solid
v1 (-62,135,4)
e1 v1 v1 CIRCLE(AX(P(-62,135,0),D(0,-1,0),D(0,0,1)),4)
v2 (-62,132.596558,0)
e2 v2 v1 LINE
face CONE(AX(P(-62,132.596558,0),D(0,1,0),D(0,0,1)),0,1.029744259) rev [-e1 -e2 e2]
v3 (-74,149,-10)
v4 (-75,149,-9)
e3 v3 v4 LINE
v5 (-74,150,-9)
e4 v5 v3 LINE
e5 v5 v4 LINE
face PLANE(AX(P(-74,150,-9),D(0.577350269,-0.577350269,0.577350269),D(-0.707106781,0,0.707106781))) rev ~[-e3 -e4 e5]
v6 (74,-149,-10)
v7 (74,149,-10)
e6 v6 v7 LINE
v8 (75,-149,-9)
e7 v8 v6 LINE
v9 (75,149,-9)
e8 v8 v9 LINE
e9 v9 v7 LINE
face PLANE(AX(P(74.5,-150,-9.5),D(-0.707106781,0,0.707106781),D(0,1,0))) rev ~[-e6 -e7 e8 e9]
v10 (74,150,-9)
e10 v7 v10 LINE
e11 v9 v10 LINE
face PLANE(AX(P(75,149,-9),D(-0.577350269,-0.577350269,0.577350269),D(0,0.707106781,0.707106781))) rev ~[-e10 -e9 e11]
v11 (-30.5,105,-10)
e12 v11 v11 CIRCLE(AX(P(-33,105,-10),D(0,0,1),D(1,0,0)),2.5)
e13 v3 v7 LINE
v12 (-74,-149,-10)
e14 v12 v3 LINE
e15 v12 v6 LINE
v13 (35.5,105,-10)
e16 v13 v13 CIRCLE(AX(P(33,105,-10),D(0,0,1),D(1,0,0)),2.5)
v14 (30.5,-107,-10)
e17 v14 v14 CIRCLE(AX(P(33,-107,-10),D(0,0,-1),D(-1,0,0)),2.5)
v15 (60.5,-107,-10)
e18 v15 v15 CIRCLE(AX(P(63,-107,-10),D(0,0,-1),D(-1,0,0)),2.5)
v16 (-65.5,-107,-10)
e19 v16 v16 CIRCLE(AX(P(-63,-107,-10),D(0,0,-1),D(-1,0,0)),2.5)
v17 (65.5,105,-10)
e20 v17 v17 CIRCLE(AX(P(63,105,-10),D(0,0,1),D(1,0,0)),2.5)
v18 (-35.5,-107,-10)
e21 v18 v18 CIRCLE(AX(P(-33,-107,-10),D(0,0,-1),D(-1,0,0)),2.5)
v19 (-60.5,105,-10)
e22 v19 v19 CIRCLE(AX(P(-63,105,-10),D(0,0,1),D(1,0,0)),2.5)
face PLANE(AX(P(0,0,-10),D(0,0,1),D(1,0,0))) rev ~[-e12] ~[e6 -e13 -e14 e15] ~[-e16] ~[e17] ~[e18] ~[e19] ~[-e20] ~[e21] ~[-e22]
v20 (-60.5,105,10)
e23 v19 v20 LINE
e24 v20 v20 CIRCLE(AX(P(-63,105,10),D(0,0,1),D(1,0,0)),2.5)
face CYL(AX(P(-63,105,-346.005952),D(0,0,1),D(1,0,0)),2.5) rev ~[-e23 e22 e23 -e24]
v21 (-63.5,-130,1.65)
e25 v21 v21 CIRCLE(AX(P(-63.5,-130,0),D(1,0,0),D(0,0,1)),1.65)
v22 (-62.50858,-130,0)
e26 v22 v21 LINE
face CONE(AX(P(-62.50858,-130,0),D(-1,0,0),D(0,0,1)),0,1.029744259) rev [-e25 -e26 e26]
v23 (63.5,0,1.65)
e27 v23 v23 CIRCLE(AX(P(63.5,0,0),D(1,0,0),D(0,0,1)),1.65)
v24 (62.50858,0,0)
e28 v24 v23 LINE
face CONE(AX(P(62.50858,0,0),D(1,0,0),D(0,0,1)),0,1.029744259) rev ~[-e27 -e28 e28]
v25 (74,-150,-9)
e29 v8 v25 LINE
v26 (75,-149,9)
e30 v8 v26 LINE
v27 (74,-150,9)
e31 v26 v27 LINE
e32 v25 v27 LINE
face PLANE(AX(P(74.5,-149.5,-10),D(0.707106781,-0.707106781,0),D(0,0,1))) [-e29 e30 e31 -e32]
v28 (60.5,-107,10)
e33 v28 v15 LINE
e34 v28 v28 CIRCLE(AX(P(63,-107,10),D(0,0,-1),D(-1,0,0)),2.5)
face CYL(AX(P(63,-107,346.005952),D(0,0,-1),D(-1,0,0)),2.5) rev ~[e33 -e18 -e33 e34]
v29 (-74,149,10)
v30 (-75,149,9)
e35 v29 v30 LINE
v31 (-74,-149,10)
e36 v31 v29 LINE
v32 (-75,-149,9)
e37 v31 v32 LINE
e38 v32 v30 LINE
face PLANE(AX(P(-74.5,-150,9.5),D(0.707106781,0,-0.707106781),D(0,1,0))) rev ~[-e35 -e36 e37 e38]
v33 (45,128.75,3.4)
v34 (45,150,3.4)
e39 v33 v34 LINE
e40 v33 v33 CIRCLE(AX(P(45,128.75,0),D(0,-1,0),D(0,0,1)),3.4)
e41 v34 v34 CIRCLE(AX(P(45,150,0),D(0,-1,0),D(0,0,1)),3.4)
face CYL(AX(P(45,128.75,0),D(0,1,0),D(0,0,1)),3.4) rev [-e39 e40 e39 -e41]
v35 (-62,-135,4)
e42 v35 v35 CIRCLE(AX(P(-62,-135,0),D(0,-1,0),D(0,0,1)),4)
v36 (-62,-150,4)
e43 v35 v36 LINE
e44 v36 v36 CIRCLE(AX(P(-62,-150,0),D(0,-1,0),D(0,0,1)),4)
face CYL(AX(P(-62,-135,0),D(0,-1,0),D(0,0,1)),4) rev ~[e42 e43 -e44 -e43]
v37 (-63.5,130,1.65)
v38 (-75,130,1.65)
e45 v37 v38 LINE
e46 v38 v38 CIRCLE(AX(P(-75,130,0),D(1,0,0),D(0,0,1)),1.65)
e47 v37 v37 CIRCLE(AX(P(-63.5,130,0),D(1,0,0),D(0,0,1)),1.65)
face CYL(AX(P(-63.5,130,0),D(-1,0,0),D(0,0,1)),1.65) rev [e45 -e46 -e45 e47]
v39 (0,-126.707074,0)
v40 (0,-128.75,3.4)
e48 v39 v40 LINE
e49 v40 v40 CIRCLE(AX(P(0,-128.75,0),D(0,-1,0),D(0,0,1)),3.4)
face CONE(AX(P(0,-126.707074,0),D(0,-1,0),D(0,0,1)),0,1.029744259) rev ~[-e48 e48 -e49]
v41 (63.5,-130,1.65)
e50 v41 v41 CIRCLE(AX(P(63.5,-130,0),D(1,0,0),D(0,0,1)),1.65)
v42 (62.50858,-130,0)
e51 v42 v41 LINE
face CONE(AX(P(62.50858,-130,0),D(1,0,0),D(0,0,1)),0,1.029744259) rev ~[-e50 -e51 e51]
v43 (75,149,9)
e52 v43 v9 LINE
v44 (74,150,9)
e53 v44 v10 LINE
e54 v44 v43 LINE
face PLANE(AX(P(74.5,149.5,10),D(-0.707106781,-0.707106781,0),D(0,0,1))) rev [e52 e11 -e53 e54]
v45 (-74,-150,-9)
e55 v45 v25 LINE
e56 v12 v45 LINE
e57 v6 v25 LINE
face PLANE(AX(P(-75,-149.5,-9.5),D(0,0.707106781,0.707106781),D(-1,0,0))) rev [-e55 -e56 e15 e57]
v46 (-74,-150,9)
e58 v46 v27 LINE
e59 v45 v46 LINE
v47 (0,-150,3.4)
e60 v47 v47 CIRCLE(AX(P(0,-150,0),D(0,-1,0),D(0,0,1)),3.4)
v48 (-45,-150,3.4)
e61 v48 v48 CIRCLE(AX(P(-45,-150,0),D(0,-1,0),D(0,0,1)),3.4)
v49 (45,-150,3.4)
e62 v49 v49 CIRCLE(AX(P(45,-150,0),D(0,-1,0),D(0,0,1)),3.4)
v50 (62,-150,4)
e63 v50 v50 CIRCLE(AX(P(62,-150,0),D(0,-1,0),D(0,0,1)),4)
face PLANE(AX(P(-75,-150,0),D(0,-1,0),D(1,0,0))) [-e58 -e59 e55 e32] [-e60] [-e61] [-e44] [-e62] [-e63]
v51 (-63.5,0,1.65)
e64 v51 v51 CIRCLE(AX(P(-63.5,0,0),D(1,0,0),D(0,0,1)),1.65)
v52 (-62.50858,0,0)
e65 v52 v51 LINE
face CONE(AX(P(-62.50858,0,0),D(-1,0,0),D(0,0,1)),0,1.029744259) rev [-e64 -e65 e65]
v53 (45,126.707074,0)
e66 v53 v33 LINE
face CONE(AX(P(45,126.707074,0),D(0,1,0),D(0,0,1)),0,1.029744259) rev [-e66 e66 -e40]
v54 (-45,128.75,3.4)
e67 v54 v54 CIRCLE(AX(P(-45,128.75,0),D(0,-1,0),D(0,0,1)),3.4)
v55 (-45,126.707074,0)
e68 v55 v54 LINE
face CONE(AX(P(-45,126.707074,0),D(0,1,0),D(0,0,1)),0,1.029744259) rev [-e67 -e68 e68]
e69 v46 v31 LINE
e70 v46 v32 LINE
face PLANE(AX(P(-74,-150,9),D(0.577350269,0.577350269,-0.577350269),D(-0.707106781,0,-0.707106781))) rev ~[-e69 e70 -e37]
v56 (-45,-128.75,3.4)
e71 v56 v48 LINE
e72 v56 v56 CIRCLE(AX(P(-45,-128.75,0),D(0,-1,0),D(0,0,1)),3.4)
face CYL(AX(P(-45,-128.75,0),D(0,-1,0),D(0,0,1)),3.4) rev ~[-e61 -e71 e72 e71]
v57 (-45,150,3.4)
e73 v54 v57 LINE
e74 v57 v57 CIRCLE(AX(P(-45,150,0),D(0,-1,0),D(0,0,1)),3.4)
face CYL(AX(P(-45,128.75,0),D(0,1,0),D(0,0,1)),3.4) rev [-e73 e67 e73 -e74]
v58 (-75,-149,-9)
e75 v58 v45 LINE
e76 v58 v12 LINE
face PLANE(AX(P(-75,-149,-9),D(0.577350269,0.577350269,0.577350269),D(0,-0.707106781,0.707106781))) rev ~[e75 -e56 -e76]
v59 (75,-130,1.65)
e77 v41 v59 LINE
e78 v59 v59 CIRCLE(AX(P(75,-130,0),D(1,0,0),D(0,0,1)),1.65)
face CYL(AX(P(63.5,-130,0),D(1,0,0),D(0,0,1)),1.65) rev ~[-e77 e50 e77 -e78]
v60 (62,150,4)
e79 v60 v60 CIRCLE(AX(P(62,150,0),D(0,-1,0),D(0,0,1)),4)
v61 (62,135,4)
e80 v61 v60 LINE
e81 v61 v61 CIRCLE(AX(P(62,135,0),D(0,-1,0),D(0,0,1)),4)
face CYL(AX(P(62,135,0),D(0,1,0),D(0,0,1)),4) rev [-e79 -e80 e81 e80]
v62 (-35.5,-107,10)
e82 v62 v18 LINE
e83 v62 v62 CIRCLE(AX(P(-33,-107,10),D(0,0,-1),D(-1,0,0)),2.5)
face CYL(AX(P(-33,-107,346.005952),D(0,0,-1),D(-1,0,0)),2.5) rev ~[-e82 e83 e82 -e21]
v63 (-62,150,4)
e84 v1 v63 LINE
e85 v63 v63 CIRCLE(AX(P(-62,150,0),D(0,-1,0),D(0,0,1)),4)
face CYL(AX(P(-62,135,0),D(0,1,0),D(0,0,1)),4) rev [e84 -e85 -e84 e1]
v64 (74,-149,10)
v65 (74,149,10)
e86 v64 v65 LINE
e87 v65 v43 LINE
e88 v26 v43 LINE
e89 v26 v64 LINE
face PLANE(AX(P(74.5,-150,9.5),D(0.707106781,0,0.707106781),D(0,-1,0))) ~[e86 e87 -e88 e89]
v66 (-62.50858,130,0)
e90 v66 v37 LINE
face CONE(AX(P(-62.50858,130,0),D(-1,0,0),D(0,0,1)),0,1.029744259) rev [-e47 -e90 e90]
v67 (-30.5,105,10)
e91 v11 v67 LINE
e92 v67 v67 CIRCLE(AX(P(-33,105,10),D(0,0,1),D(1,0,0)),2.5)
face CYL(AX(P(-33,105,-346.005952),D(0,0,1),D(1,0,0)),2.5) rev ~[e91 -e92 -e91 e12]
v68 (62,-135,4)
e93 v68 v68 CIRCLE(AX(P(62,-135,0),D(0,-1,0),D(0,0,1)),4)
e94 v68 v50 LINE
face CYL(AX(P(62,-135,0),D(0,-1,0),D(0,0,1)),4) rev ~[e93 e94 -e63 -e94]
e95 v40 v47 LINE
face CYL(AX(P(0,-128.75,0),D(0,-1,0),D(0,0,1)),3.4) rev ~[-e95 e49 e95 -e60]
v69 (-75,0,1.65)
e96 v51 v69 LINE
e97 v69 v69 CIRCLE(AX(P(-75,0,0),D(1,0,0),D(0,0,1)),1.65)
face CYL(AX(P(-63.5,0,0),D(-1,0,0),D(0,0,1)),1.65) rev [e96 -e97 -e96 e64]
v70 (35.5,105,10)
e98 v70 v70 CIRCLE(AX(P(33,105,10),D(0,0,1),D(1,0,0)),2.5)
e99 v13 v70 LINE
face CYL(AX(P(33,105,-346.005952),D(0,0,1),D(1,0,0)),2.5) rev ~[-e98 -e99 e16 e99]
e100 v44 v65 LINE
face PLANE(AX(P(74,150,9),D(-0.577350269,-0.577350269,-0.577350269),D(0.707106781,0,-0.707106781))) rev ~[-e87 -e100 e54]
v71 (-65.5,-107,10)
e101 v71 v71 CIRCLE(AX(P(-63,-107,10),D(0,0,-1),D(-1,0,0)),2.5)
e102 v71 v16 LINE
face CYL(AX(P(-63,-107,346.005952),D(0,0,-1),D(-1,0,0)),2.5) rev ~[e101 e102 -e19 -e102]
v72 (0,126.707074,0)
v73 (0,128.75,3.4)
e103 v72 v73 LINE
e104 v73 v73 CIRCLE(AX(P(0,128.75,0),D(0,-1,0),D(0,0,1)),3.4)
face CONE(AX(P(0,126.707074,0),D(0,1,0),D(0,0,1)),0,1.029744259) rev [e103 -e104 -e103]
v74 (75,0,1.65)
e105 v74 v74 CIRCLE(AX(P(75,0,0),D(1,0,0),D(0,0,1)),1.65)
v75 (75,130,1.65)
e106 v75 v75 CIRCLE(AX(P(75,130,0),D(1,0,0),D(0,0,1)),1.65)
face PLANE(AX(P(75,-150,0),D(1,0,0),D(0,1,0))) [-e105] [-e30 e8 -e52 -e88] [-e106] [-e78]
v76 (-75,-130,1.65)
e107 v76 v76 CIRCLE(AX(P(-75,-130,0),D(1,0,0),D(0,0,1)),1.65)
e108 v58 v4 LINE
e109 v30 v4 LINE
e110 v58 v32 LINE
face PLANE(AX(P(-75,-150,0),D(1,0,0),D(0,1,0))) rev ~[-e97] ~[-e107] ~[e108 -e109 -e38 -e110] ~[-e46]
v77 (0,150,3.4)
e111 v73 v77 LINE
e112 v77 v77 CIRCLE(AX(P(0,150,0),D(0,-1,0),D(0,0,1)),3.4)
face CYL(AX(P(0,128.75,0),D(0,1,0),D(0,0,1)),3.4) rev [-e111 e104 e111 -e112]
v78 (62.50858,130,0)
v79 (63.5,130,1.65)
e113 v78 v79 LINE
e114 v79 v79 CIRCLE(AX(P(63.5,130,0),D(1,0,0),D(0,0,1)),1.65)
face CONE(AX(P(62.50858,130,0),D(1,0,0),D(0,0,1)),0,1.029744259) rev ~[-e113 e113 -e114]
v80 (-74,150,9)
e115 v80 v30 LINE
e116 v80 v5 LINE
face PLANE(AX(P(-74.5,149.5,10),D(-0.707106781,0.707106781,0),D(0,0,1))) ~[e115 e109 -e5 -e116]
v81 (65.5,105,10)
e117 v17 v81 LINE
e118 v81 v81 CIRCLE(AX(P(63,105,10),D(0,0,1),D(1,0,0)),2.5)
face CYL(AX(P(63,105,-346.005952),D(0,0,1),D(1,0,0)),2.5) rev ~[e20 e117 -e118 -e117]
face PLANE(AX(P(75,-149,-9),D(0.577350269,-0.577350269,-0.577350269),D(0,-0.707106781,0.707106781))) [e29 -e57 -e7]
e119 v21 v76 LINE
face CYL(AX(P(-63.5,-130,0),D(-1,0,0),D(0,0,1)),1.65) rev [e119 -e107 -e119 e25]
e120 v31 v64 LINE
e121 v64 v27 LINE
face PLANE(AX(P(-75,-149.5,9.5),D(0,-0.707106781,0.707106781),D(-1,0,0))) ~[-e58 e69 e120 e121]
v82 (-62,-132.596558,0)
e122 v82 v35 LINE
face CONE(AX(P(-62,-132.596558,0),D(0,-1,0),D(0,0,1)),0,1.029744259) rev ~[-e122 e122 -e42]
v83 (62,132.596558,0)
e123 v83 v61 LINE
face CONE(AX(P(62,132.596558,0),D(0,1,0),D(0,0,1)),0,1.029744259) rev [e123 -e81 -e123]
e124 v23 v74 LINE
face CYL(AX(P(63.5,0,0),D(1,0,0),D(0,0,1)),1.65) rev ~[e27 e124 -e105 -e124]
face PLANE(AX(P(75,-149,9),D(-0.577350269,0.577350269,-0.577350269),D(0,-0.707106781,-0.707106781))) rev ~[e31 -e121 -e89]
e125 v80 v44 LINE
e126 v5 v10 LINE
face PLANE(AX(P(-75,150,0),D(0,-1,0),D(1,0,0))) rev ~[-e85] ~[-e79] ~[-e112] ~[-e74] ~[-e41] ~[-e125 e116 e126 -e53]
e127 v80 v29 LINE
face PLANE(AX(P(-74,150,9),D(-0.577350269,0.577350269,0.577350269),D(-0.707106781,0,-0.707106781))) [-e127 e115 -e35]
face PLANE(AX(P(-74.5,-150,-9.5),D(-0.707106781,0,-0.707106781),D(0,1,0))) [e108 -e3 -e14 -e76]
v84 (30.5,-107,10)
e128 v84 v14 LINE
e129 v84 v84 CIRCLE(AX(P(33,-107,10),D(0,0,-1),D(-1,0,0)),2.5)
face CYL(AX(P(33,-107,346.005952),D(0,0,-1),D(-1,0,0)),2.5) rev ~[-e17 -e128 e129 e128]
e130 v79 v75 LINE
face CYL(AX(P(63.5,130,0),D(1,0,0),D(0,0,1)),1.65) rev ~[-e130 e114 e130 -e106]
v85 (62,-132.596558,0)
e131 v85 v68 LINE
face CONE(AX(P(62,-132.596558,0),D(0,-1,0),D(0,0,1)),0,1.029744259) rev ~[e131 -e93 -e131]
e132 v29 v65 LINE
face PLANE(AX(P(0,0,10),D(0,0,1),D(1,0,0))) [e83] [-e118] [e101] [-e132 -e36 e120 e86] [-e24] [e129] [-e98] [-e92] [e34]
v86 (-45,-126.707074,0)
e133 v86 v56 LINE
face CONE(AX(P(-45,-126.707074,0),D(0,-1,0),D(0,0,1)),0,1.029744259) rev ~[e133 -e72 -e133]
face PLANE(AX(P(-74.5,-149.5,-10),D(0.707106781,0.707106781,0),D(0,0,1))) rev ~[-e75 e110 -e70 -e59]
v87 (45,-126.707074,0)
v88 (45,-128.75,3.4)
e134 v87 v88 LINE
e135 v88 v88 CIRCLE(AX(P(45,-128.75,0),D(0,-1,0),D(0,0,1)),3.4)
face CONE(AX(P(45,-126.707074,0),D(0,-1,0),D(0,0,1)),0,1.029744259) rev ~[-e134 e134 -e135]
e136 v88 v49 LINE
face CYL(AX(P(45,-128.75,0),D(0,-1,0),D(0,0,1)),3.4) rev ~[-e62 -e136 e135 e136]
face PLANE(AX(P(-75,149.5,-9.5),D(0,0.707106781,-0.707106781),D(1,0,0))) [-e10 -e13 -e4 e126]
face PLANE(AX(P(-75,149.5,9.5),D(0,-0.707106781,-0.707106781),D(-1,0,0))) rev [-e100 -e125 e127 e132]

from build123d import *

# Parameters (mm, degrees)
SKETCH_1_W                  = 150
SKETCH_1_H                  = 300
EXTRUDE_1_DEPTH             = 10
CHAMFER_1_SIZE              = 1
HOLE_WIZARD_M8_1_AT_2_COUNT = 2
HOLE_WIZARD_M8_1_AT_2_PITCH = 90
HOLE_WIZARD_M8_1_AT_3_COUNT = 2
HOLE_WIZARD_M8_1_AT_3_PITCH = 45
HOLE_WIZARD_M4_1_AT_2_COUNT = 2
HOLE_WIZARD_M4_1_AT_2_PITCH = 130
HOLE_WIZARD_M4_1_AT_3_COUNT = 2
HOLE_WIZARD_M4_1_AT_3_PITCH = 260
MM_1_AT_2_COUNT             = 2
MM_1_AT_2_PITCH             = 124
HOLE_WIZARD_M6_3_D          = 5
HOLE_WIZARD_M6_4_D          = 5


with BuildPart() as part:
    # 草图1 → 凸台-拉伸1 (new, symmetric)
    with BuildSketch(Plane.XY):
        Rectangle(SKETCH_1_W, SKETCH_1_H)
    extrude(amount=EXTRUDE_1_DEPTH, both=True)

    # 倒角1
    chamfer_1_edges = [part.edges().sort_by_distance(p)[0] for p in [
        (-75, 0, 10),
        (0, -150, 10),
        (75, 0, 10),
        (0, -150, -10),
        (-75, 0, -10),
        (0, 150, -10),
        (75, 0, -10),
        (0, 150, 10),
        (75, -150, 0),
        (-75, -150, 0),
        (-75, 150, 0),
        (75, 150, 0),
    ]]
    chamfer(chamfer_1_edges, length=CHAMFER_1_SIZE)

    # 草图2 → M8 螺纹孔1 (revolve, cut)
    with BuildSketch(Plane(origin=(-45, 150, 0), x_dir=(0, 0, 1), z_dir=(1, 0, 0))):
        Polygon((0, 0), (0, 23.292926105), (3.4, 21.25), (3.4, 0), align=None)
    hole_wizard_m8_1 = revolve(axis=Axis((-45, 156.35, 0), (0, -1, 0)), mode=Mode.SUBTRACT)

    # M8 螺纹孔1 at 2: M8 螺纹孔1 ×2
    with Locations(*[(i * HOLE_WIZARD_M8_1_AT_2_PITCH, 0, 0) for i in range(1, HOLE_WIZARD_M8_1_AT_2_COUNT)]):
        add(hole_wizard_m8_1, mode=Mode.SUBTRACT)

    # M8 螺纹孔1 at 3: M8 螺纹孔1 ×2
    with Locations(*[(i * HOLE_WIZARD_M8_1_AT_3_PITCH, 0, 0) for i in range(1, HOLE_WIZARD_M8_1_AT_3_COUNT)]):
        add(hole_wizard_m8_1, mode=Mode.SUBTRACT)

    # 草图10 → M4 螺纹孔1 (revolve, cut)
    with BuildSketch(Plane(origin=(-75, -130, 0), x_dir=(0, 0, 1), z_dir=(0, 1, 0))):
        Polygon((0, 0), (0, 12.491420021), (1.65, 11.5), (1.65, 0), align=None)
    hole_wizard_m4_1 = revolve(axis=Axis((-81.35, -130, 0), (1, 0, 0)), mode=Mode.SUBTRACT)

    # M4 螺纹孔1 at 2: M4 螺纹孔1 ×2
    with Locations(*[(0, i * HOLE_WIZARD_M4_1_AT_2_PITCH, 0) for i in range(1, HOLE_WIZARD_M4_1_AT_2_COUNT)]):
        add(hole_wizard_m4_1, mode=Mode.SUBTRACT)

    # M4 螺纹孔1 at 3: M4 螺纹孔1 ×2
    with Locations(*[(0, i * HOLE_WIZARD_M4_1_AT_3_PITCH, 0) for i in range(1, HOLE_WIZARD_M4_1_AT_3_COUNT)]):
        add(hole_wizard_m4_1, mode=Mode.SUBTRACT)

    # 镜向1: M4 螺纹孔1 across plane
    add(hole_wizard_m4_1.mirror(Plane(origin=(0, 0, 0), x_dir=(0, 0, 1), z_dir=(1, 0, 0))), mode=Mode.SUBTRACT)

    # 镜向1 copy 1 sketch → 镜向1 copy 1 (revolve, cut)
    with BuildSketch(Plane(origin=(75, 0, 0), x_dir=(0, 0, 1), z_dir=(0, 1, 0))):
        Polygon((0, 0), (0, -12.491420021), (1.65, -11.5), (1.65, 0), align=None)
    revolve(axis=Axis((81.35, 0, 0), (1, 0, 0)), mode=Mode.SUBTRACT)

    # 镜向1 copy 2 sketch → 镜向1 copy 2 (revolve, cut)
    with BuildSketch(Plane(origin=(75, 130, 0), x_dir=(0, 0, 1), z_dir=(0, 1, 0))):
        Polygon((0, 0), (0, -12.491420021), (1.65, -11.5), (1.65, 0), align=None)
    revolve(axis=Axis((81.35, 130, 0), (1, 0, 0)), mode=Mode.SUBTRACT)

    # 草图16 → 大小mm 暗销孔1 (revolve, cut)
    with BuildSketch(Plane(origin=(-62, 150, 0), x_dir=(0, 0, 1), z_dir=(1, 0, 0))):
        Polygon((0, 0), (0, 17.403442476), (4, 15), (4, 0), align=None)
    mm_1 = revolve(axis=Axis((-62, 156.35, 0), (0, -1, 0)), mode=Mode.SUBTRACT)

    # 大小mm 暗销孔1 at 2: 大小mm 暗销孔1 ×2
    with Locations(*[(i * MM_1_AT_2_PITCH, 0, 0) for i in range(1, MM_1_AT_2_COUNT)]):
        add(mm_1, mode=Mode.SUBTRACT)

    # M6 螺纹孔3 (through all)
    with Locations(Plane(origin=(0, 0, -10), x_dir=(-1, 0, 0), z_dir=(0, 0, -1))):
        with Locations((-33, 105), (-63, 105), (63, 105), (33, 105)):
            Hole(HOLE_WIZARD_M6_3_D / 2)

    # M6 螺纹孔4 (through all)
    with Locations(Plane.XY.offset(10)):
        with Locations((-33, -107), (-63, -107), (33, -107), (63, -107)):
            Hole(HOLE_WIZARD_M6_4_D / 2)

    # 镜向2: M8 螺纹孔1, 大小mm 暗销孔1 across plane
    add(hole_wizard_m8_1.mirror(Plane.ZX), mode=Mode.SUBTRACT)
    add(mm_1.mirror(Plane.ZX), mode=Mode.SUBTRACT)

    # 镜向2 copy 1 sketch → 镜向2 copy 1 (revolve, cut)
    with BuildSketch(Plane(origin=(45, -150, 0), x_dir=(0, 0, 1), z_dir=(1, 0, 0))):
        Polygon((0, 0), (0, -23.292926105), (3.4, -21.25), (3.4, 0), align=None)
    revolve(axis=Axis((45, -156.35, 0), (0, -1, 0)), mode=Mode.SUBTRACT)

    # 镜向2 copy 2 sketch → 镜向2 copy 2 (revolve, cut)
    with BuildSketch(Plane(origin=(0, -150, 0), x_dir=(0, 0, 1), z_dir=(1, 0, 0))):
        Polygon((0, 0), (0, -23.292926105), (3.4, -21.25), (3.4, 0), align=None)
    revolve(axis=Axis((0, -156.35, 0), (0, -1, 0)), mode=Mode.SUBTRACT)

    # 镜向2 copy 3 sketch → 镜向2 copy 3 (revolve, cut)
    with BuildSketch(Plane(origin=(62, -150, 0), x_dir=(0, 0, 1), z_dir=(1, 0, 0))):
        Polygon((0, 0), (0, -17.403442476), (4, -15), (4, 0), align=None)
    revolve(axis=Axis((62, -156.35, 0), (0, -1, 0)), mode=Mode.SUBTRACT)


solid = part.part
